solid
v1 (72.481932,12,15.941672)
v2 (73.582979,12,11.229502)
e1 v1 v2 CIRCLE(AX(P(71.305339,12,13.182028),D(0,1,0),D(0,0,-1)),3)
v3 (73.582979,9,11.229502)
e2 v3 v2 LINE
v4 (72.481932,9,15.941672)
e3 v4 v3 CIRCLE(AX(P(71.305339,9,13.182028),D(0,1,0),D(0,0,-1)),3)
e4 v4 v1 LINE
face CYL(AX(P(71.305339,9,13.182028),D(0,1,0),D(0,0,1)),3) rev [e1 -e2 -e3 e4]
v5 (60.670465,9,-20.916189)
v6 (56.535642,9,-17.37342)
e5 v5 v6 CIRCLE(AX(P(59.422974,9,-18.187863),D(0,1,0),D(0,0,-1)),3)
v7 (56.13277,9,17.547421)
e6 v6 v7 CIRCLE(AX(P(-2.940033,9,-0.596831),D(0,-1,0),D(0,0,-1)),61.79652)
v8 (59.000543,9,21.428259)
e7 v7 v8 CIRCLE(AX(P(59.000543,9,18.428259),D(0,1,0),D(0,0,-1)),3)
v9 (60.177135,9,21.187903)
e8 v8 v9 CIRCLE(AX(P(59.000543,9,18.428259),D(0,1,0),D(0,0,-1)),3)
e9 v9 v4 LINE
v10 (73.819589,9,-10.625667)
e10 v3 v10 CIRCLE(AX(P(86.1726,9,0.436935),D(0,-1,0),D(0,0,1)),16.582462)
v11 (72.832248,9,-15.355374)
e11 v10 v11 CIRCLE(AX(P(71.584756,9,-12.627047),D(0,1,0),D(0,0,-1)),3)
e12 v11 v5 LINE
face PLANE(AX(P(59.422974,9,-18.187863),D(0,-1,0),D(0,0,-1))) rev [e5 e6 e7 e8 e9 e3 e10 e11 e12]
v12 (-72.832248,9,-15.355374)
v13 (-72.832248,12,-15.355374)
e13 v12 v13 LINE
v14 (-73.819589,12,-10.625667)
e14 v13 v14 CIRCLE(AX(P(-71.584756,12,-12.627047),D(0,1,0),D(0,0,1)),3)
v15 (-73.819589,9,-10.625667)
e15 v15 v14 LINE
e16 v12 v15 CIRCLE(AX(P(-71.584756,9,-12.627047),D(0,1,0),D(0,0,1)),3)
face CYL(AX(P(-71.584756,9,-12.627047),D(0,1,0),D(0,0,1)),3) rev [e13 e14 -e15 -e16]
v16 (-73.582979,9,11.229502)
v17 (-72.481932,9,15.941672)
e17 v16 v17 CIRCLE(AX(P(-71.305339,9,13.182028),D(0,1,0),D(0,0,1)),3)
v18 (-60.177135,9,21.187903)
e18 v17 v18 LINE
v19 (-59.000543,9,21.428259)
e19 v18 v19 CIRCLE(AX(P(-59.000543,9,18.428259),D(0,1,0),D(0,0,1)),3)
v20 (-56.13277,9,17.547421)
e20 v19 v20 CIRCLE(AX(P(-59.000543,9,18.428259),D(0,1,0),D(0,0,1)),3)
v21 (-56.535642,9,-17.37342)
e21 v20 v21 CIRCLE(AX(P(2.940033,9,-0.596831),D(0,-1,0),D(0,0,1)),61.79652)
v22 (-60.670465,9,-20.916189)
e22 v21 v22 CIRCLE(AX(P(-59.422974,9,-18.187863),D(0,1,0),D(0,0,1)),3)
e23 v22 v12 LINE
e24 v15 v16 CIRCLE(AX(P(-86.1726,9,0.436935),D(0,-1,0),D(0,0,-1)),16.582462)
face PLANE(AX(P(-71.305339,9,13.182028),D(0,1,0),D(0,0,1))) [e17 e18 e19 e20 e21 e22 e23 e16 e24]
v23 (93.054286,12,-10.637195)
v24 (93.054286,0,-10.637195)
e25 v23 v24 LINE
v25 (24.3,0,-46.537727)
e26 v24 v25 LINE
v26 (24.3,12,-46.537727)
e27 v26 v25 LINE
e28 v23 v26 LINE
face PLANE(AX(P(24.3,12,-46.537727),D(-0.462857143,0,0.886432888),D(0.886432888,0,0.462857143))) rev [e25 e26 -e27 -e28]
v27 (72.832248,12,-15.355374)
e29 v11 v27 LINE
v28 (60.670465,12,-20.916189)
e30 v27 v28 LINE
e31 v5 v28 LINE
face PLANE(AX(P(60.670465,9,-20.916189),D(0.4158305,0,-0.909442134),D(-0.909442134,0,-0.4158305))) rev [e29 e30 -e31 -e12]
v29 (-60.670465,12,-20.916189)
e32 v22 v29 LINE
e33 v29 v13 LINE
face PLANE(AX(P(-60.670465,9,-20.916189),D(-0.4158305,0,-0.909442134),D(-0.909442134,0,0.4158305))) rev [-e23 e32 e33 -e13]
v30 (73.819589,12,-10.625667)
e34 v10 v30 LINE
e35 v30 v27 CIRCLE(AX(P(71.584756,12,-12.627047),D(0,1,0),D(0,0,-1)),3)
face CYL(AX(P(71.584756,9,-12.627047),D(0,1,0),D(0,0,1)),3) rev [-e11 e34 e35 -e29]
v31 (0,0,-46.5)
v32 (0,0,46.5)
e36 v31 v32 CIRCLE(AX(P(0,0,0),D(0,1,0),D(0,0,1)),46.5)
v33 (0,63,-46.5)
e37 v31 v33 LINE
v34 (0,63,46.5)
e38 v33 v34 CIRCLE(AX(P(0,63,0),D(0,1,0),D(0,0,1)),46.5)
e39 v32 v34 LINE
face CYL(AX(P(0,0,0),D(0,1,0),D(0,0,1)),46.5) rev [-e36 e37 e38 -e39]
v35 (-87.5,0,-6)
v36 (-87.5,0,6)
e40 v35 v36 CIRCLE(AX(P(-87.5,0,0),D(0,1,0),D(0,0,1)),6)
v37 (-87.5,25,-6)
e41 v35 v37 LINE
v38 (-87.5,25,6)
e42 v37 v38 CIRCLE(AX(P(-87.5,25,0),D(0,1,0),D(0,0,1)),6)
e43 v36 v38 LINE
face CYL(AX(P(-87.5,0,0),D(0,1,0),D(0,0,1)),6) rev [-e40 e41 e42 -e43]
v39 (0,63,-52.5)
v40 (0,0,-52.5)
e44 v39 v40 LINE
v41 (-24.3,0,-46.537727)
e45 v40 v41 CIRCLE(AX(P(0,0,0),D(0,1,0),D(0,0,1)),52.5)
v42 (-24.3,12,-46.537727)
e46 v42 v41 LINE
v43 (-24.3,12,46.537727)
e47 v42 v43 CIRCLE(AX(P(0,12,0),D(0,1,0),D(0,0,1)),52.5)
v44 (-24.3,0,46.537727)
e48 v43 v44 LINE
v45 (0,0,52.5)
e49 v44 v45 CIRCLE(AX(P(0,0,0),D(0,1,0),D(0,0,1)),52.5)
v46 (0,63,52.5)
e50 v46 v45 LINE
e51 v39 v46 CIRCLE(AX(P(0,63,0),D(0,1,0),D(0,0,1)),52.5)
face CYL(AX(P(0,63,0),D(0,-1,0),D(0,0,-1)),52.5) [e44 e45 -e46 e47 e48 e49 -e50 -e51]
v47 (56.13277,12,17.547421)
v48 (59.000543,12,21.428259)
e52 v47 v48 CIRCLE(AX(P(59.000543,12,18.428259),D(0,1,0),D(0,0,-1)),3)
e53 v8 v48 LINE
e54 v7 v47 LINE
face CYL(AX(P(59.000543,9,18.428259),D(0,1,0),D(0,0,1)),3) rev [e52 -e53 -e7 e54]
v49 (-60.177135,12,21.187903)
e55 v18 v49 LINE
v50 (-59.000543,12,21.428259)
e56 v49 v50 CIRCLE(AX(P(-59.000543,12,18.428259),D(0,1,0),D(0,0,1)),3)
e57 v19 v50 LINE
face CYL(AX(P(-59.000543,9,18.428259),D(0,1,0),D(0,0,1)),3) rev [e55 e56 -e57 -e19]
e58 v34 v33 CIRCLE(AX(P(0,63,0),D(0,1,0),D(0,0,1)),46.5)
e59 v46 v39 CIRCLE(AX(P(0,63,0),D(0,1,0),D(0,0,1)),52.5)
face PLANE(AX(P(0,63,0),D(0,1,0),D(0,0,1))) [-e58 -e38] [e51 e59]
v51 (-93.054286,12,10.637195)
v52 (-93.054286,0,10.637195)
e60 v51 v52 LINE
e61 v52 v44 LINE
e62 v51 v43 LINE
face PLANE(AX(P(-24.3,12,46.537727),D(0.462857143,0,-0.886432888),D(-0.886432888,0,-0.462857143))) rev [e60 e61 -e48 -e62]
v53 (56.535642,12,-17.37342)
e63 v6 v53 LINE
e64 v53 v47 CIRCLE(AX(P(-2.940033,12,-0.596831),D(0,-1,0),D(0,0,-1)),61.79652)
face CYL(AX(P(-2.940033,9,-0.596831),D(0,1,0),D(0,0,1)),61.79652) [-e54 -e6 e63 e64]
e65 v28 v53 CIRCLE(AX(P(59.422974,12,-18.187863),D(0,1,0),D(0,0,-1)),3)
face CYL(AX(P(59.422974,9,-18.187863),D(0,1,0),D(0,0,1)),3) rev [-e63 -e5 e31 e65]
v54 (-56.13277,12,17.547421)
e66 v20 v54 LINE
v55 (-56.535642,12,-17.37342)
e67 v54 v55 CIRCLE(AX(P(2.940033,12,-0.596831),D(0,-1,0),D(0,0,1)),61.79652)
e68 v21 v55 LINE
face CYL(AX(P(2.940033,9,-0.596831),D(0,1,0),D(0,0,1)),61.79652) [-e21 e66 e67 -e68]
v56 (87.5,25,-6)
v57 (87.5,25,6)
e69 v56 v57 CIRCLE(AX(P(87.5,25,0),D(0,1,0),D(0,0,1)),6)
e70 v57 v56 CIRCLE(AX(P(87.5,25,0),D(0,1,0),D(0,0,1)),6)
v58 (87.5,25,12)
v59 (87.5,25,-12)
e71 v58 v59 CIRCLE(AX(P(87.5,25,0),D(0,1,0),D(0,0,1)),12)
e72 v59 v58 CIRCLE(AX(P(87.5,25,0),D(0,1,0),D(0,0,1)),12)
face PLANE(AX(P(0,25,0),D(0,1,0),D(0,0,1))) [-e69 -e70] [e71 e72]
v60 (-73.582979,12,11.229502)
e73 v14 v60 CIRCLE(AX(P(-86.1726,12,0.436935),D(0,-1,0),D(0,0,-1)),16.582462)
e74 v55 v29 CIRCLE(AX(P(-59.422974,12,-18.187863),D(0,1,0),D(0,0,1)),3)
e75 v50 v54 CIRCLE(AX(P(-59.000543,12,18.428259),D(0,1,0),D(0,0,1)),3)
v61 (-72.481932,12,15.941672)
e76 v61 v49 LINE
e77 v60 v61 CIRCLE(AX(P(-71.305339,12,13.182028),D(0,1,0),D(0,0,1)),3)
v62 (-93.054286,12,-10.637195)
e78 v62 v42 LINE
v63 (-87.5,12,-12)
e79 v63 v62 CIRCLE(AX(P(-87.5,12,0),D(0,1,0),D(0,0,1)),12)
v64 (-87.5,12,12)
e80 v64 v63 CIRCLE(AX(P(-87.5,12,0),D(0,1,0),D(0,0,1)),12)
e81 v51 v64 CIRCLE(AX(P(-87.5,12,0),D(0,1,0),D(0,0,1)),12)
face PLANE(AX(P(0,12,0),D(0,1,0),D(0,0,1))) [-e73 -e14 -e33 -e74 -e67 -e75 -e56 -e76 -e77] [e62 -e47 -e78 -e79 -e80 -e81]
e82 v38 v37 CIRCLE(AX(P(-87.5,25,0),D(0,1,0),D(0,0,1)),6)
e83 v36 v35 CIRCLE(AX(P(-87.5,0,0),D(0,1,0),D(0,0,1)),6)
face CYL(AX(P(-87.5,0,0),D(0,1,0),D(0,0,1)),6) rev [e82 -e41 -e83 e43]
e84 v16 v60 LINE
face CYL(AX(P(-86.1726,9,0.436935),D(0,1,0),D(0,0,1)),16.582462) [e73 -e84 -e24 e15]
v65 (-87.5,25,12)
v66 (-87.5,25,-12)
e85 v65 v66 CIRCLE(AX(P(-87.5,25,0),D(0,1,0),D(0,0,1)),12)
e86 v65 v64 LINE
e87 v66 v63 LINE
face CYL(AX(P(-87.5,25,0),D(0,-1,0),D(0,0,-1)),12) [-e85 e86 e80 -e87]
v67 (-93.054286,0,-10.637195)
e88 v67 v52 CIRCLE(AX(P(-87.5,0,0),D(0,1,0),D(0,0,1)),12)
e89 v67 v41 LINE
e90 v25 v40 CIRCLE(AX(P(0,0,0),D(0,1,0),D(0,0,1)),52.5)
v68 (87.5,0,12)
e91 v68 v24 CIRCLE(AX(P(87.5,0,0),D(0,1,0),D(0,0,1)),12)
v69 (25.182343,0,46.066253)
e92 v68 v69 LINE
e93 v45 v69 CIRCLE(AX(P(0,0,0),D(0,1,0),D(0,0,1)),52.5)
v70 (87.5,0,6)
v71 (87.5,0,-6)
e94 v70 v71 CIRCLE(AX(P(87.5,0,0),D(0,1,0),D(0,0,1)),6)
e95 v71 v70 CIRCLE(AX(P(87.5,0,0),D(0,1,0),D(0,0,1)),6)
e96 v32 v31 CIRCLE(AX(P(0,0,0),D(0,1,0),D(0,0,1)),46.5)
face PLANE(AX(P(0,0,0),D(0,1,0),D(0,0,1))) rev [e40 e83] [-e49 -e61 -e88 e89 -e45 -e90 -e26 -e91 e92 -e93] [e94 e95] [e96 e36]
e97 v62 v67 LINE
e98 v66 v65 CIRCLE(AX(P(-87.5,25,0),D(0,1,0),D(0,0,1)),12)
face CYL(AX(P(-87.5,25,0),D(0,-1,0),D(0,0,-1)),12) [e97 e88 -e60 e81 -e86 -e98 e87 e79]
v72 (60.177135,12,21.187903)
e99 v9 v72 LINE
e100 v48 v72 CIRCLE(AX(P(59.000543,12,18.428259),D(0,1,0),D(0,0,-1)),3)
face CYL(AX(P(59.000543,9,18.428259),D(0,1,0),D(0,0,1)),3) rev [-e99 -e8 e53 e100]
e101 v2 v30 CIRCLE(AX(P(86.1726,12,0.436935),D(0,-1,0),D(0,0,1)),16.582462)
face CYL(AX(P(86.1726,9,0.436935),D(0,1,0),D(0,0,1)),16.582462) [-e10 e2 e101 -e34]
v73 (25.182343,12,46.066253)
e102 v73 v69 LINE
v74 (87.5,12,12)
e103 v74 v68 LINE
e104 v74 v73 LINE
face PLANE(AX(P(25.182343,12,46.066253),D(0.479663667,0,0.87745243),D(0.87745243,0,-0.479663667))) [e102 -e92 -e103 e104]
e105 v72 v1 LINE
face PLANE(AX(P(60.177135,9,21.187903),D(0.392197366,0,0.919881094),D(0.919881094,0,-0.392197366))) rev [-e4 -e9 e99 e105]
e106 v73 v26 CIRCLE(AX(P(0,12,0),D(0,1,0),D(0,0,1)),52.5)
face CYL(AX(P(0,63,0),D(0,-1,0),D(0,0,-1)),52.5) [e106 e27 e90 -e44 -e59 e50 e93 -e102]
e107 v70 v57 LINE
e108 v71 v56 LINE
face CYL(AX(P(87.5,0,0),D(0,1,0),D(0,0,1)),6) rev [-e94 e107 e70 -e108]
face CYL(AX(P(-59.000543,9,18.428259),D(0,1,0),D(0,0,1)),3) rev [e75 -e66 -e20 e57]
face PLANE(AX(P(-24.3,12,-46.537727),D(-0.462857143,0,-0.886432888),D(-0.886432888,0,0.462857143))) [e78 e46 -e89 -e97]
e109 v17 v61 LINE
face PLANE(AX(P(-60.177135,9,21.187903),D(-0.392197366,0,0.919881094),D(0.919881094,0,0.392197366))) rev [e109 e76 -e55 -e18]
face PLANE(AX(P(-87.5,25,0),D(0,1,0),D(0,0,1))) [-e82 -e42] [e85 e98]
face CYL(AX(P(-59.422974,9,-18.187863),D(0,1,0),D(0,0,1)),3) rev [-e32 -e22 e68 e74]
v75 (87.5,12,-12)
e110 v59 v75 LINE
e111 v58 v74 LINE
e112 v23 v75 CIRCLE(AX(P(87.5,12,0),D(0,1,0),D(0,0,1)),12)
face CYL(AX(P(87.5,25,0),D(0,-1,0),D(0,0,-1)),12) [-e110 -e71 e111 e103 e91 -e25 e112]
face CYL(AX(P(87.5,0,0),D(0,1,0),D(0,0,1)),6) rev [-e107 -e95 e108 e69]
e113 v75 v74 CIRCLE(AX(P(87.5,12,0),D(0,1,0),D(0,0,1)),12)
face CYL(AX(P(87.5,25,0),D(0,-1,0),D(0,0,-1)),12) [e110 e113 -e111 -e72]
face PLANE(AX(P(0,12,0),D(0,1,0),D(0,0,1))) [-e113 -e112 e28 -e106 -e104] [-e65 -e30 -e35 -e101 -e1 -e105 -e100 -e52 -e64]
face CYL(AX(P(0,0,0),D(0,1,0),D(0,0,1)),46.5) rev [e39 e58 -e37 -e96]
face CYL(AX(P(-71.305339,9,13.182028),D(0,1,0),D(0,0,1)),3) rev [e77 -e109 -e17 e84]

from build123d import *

# Parameters (mm, degrees)
HOUSING_BASE_PROFILE_SKETCH_R  = 52.5
HOUSING_CYLINDER_DEPTH         = 63
MOUNTING_FLANGE_DEPTH          = 12
SKETCH1_4_R                    = 12
LUG_BOSSES_DEPTH               = 25
BORE_AND_LUG_HOLES_SKETCH_R    = 6
BORE_AND_LUG_HOLES_SKETCH_R_2  = 46.5
BORE_AND_LUG_HOLES_2X_12_DEPTH = 129.939908485
FLANGE_RELIEF_POCKETS_DEPTH    = 3


with BuildPart() as part:
    # Housing Base Profile Sketch → Housing Cylinder (new body)
    with BuildSketch(Plane(origin=(0, 0, 0), x_dir=(1, 0, 0), z_dir=(0, 1, 0))):
        with Locations(Location((0, 0, 0), (0, 0, 270))):
            Circle(HOUSING_BASE_PROFILE_SKETCH_R)
    extrude(amount=HOUSING_CYLINDER_DEPTH)

    # Sketch1_3 → Mounting Flange (add)
    with BuildSketch(Plane(origin=(0, 0, 0), x_dir=(1, 0, 0), z_dir=(0, 1, 0))):
        with BuildLine():
            Line((-24.3, 46.537726631), (-93.054285714, 10.637194659))
            ThreePointArc((-93.054285714, 10.637194659), (-81.281134692, 10.262831689), (-75.5, 0))
            ThreePointArc((-75.5, 0), (-81.281134692, -10.262831689), (-93.054285714, -10.637194659))
            Line((-93.054285714, -10.637194659), (-24.3, -46.537726631))
            ThreePointArc((-24.3, -46.537726631), (-52.5, 0), (-24.3, 46.537726631))
        make_face()
        with BuildLine():
            Line((93.054285714, 10.637194659), (24.3, 46.537726631))
            ThreePointArc((24.3, 46.537726631), (44.899888641, 27.207535721), (52.5, 0))
            ThreePointArc((52.5, 0), (45.157075755, -26.778508346), (25.182342504, -46.066252572))
            Line((25.182342504, -46.066252572), (87.5, -12))
            ThreePointArc((87.5, -12), (75.845680288, 2.859516051), (93.054285714, 10.637194659))
        make_face()
    extrude(amount=MOUNTING_FLANGE_DEPTH)

    # Sketch1_4 → Lug Bosses (add)
    with BuildSketch(Plane(origin=(0, 0, 0), x_dir=(1, 0, 0), z_dir=(0, 1, 0))):
        with Locations(Location((87.5, 0, 0), (0, 0, 270))):
            Circle(SKETCH1_4_R)
        with Locations(Location((-87.5, 0, 0), (0, 0, 117.57162794))):
            Circle(SKETCH1_4_R)
    extrude(amount=LUG_BOSSES_DEPTH)

    # Bore and Lug Holes Sketch → Bore and Lug Holes 2x_12 (cut, through all)
    with BuildSketch(Plane(origin=(0, 63, 0), x_dir=(1, 0, 0), z_dir=(0, 1, 0))):
        with Locations(Location((-87.5, 0, 0), (0, 0, 270))):
            Circle(BORE_AND_LUG_HOLES_SKETCH_R)
        with Locations(Location((0, 0, 0), (0, 0, 270))):
            Circle(BORE_AND_LUG_HOLES_SKETCH_R_2)
        with Locations(Location((87.5, 0, 0), (0, 0, 270))):
            Circle(BORE_AND_LUG_HOLES_SKETCH_R)
    extrude(amount=-BORE_AND_LUG_HOLES_2X_12_DEPTH, mode=Mode.SUBTRACT)

    # Flange Pockets Sketch → Flange Relief Pockets (cut)
    with BuildSketch(Plane(origin=(0, 12, 0), x_dir=(1, 0, 0), z_dir=(0, 1, 0))):
        with BuildLine():
            Line((-60.67046514, 20.916189471), (-72.83224793, 15.355373632))
            ThreePointArc((-72.83224793, 15.355373632), (-74.521451253, 13.240091694), (-73.819589316, 10.625667214))
            ThreePointArc((-73.819589316, 10.625667214), (-69.591109503, -0.257419194), (-73.582978557, -11.22950162))
            ThreePointArc((-73.582978557, -11.22950162), (-74.226651592, -13.864622877), (-72.481931561, -15.941671512))
            Line((-72.481931561, -15.941671512), (-60.177135194, -21.187902521))
            ThreePointArc((-60.177135194, -21.187902521), (-56.993480479, -20.657990086), (-56.132769828, -17.547420732))
            ThreePointArc((-56.132769828, -17.547420732), (-58.852375063, -0.116051975), (-56.53564235, 17.373419684))
            ThreePointArc((-56.53564235, 17.373419684), (-57.471032791, 20.466004181), (-60.67046514, 20.916189471))
        make_face()
        with BuildLine():
            Line((60.67046514, 20.916189471), (72.83224793, 15.355373632))
            ThreePointArc((72.83224793, 15.355373632), (74.521451253, 13.240091694), (73.819589316, 10.625667214))
            ThreePointArc((73.819589316, 10.625667214), (69.591109503, -0.257419194), (73.582978557, -11.22950162))
            ThreePointArc((73.582978557, -11.22950162), (74.226651592, -13.864622877), (72.481931561, -15.941671512))
            Line((72.481931561, -15.941671512), (60.177135194, -21.187902521))
            ThreePointArc((60.177135194, -21.187902521), (56.993480479, -20.657990086), (56.132769828, -17.547420732))
            ThreePointArc((56.132769828, -17.547420732), (58.852375063, -0.116051975), (56.53564235, 17.373419684))
            ThreePointArc((56.53564235, 17.373419684), (57.471032791, 20.466004181), (60.67046514, 20.916189471))
        make_face()
    extrude(amount=-FLANGE_RELIEF_POCKETS_DEPTH, mode=Mode.SUBTRACT)


solid = part.part
